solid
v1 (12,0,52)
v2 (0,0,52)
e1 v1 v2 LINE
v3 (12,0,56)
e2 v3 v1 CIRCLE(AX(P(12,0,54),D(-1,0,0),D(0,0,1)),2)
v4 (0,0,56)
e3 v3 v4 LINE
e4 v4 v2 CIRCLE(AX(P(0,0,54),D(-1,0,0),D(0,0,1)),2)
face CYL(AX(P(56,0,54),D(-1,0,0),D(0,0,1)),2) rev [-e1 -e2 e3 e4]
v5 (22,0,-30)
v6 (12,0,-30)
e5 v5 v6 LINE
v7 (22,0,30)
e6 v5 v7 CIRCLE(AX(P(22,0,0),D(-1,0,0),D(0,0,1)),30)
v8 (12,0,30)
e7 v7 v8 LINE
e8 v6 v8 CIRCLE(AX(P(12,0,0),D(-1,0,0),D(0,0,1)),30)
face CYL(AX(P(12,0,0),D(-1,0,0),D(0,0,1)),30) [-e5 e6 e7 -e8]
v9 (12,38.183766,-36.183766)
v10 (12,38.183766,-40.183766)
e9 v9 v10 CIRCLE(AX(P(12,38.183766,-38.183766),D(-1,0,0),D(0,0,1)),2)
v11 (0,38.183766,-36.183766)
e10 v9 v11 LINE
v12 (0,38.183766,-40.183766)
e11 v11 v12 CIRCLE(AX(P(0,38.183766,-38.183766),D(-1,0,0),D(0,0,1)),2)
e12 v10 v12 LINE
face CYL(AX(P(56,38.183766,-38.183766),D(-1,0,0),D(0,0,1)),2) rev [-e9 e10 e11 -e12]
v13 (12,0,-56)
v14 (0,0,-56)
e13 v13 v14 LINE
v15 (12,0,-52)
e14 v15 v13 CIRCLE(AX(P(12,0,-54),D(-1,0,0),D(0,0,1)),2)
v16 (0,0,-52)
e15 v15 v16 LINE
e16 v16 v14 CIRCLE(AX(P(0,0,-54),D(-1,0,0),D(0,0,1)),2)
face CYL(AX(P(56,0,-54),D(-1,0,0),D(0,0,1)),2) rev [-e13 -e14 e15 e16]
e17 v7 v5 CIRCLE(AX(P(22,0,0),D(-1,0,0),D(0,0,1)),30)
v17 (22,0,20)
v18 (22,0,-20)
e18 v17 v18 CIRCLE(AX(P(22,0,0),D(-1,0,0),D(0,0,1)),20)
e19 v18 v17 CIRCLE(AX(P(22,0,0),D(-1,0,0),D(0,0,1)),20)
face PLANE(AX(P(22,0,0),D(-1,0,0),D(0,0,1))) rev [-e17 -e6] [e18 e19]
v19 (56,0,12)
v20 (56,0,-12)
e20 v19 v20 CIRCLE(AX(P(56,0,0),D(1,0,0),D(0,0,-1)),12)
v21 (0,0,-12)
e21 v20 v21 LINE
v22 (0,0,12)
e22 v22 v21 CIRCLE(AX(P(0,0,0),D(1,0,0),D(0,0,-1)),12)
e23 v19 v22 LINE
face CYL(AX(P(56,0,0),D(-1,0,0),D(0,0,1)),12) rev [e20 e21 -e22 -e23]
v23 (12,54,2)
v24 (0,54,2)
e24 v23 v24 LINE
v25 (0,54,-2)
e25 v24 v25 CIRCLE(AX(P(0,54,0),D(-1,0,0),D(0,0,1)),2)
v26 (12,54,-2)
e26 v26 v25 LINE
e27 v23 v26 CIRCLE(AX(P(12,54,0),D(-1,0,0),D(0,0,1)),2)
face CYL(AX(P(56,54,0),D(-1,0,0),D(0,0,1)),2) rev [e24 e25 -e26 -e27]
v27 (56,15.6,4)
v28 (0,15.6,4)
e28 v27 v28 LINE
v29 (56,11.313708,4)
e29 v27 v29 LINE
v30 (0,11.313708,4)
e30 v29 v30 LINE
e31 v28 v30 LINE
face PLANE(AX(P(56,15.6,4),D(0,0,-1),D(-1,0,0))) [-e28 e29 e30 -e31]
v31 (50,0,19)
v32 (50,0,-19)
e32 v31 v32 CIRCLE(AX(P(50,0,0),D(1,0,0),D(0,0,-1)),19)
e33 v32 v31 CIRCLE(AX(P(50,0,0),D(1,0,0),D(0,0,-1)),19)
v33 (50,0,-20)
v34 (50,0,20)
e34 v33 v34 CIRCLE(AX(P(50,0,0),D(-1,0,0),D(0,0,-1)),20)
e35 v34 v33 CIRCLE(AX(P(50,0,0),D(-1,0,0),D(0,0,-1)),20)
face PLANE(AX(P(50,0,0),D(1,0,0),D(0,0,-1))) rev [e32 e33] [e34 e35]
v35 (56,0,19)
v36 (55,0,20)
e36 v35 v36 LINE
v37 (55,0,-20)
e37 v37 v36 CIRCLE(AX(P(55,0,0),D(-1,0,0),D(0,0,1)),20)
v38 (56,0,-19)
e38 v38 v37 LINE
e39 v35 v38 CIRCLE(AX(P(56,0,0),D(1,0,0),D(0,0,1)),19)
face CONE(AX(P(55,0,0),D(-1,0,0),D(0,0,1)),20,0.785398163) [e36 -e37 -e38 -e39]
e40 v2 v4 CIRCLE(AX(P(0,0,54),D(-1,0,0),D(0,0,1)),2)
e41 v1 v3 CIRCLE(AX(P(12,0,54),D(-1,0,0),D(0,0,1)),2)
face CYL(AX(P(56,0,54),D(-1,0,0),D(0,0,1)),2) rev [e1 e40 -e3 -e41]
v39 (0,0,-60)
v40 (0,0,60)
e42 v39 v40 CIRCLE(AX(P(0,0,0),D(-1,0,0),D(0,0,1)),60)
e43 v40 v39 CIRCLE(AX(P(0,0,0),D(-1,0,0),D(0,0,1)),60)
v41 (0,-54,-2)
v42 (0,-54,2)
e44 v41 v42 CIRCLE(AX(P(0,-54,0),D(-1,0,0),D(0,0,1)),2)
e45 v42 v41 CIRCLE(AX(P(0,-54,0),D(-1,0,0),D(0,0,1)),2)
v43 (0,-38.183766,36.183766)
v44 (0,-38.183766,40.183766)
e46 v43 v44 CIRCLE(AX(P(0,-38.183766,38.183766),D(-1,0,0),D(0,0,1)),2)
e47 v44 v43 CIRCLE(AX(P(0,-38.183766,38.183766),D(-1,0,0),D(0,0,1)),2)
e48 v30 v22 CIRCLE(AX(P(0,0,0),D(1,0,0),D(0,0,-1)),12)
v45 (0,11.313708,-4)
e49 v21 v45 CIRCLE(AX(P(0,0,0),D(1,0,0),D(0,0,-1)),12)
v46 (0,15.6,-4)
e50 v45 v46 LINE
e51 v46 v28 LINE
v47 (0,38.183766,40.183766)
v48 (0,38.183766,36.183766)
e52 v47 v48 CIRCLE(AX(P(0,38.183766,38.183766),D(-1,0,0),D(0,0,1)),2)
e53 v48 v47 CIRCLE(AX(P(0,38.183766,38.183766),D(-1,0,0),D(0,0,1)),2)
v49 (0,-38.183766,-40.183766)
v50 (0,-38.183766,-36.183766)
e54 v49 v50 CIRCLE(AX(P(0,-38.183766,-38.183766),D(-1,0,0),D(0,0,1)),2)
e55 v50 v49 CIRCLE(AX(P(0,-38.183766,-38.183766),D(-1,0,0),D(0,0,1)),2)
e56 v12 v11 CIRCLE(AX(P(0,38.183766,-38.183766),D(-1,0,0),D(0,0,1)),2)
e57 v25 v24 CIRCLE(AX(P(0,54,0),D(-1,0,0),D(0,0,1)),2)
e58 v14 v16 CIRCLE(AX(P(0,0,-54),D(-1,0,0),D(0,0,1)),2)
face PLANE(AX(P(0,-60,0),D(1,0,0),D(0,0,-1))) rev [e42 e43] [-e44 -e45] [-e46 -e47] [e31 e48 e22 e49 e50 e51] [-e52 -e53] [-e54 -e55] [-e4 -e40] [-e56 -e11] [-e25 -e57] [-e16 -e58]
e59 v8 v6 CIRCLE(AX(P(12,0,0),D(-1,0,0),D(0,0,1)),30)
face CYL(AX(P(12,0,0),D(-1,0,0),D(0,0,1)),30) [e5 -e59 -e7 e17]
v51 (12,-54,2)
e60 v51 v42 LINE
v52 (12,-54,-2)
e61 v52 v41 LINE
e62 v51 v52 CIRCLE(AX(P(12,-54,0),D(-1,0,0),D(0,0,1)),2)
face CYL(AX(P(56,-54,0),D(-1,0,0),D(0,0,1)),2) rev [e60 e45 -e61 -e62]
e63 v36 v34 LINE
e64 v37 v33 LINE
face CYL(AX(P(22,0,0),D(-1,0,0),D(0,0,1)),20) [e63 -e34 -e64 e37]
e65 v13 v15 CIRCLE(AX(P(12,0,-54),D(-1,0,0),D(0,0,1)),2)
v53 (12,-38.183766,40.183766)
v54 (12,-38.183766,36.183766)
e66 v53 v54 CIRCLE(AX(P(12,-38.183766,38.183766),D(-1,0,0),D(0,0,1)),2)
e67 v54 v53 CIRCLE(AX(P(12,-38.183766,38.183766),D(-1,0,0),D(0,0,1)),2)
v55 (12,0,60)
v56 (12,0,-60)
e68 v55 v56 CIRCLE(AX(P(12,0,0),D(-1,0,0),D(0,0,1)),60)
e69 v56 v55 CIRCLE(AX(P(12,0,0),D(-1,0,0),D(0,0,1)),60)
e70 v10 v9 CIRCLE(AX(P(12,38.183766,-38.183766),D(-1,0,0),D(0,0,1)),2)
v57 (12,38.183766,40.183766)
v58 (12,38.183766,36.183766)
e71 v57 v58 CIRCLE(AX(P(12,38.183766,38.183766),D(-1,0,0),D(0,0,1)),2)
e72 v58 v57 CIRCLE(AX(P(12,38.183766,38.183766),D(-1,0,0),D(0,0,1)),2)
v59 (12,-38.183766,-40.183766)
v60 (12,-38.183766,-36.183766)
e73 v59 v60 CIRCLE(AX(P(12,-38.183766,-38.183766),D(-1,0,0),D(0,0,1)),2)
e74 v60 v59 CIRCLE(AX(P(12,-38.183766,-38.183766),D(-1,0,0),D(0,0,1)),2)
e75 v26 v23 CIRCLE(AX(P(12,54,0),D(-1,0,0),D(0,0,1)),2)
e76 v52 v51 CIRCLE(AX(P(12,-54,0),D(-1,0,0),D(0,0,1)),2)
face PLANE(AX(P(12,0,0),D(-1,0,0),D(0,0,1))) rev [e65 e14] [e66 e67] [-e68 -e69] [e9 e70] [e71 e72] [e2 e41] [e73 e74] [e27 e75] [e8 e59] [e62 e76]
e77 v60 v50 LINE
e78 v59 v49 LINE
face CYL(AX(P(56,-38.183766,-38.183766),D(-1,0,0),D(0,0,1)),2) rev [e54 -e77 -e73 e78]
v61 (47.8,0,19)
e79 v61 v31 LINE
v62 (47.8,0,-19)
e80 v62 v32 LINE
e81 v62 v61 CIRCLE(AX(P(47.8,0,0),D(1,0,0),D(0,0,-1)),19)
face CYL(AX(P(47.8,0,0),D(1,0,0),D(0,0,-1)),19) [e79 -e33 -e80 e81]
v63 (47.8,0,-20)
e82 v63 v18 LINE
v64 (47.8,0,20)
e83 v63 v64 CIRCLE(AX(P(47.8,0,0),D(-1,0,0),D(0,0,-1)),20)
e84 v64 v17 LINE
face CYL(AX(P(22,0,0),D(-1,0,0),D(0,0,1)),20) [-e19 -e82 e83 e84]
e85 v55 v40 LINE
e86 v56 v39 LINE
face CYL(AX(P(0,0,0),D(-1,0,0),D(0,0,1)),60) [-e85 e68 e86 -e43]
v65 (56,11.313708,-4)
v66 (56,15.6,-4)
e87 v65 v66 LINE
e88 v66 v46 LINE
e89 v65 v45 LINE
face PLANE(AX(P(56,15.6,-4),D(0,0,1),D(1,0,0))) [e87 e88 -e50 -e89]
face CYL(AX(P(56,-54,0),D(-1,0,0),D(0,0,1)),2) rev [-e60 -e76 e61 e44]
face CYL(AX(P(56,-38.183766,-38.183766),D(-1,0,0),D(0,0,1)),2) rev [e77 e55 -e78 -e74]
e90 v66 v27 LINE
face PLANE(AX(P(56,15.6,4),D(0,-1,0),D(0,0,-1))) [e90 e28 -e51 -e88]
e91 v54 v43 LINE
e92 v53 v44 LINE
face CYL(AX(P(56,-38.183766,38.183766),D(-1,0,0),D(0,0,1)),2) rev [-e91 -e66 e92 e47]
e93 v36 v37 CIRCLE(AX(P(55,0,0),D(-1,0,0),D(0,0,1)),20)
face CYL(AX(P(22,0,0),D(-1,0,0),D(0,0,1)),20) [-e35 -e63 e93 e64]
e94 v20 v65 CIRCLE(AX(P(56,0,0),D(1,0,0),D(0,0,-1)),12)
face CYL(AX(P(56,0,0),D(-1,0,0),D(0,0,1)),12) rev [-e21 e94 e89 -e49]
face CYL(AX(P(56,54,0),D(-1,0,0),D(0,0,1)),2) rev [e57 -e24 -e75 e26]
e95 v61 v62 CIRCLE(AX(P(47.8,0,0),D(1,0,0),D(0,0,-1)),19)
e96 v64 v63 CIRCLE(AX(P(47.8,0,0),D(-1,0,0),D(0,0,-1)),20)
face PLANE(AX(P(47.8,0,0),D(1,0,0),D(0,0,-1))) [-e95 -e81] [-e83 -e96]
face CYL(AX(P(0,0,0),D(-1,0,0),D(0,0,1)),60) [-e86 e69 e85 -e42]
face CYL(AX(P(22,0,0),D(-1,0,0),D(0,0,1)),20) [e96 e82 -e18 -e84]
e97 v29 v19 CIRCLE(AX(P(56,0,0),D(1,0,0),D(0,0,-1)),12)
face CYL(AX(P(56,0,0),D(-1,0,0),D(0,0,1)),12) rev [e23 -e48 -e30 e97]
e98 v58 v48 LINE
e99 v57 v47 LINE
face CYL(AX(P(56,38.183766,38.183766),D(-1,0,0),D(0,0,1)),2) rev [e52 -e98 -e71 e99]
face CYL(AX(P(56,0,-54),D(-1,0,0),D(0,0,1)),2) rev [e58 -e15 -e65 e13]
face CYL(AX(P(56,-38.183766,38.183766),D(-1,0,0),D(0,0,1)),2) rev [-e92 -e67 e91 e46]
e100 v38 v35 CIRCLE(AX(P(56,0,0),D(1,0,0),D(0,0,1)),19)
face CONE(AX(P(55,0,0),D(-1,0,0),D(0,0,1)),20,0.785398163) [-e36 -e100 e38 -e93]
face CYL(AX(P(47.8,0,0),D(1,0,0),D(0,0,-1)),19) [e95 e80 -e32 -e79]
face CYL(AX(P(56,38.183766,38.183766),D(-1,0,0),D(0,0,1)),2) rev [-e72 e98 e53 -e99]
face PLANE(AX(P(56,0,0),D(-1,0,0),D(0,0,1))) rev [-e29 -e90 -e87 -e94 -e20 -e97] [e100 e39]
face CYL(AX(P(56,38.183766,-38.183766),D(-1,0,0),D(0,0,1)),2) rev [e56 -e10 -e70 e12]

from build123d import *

# Parameters (mm, degrees)
SKETCH_1_W          = 12
SKETCH_1_H          = 60
SKETCH_2_W          = 10
SKETCH_2_H          = 30
SKETCH_3_W          = 34
SKETCH_3_H          = 20
CUT_EXTRUDE_2_DEPTH = 102.666120217
CUT_EXTRUDE_START   = 50
SKETCH_6_OUTSIDE_W  = 157.742
SKETCH_6_OUTSIDE_H  = 157.742
SKETCH_6_OUTSIDE_R  = 19
CUT_EXTRUDE_4_DEPTH = 2.2
SKETCH_7_R          = 2
CUT_EXTRUDE_5_DEPTH = 102.666120217
CHAMFER_2_SIZE      = 1


with BuildPart() as part:
    # 草图1 → 旋转-薄壁2 (revolve)
    with BuildSketch(Plane.XY, mode=Mode.PRIVATE) as revolve_2_sk:
        with Locations((6, 30)):
            Rectangle(SKETCH_1_W, SKETCH_1_H)
    revolve(revolve_2_sk.sketch.rotate(Axis((0, 0, 0), (1, 0, 0)), 90), axis=Axis((0, 0, 0), (1, 0, 0)))

    # 草图2 → 旋转-薄壁4 (revolve)
    with BuildSketch(Plane.XY, mode=Mode.PRIVATE) as revolve_4_sk:
        with Locations((17, 15)):
            Rectangle(SKETCH_2_W, SKETCH_2_H)
    revolve(revolve_4_sk.sketch.rotate(Axis((12, 0, 0), (1, 0, 0)), 90), axis=Axis((12, 0, 0), (1, 0, 0)))

    # 草图3 → 旋转-薄壁5 (revolve)
    with BuildSketch(Plane.XY, mode=Mode.PRIVATE) as revolve_5_sk:
        with Locations((39, 10)):
            Rectangle(SKETCH_3_W, SKETCH_3_H)
    revolve(revolve_5_sk.sketch.rotate(Axis((22, 0, 0), (1, 0, 0)), 90), axis=Axis((22, 0, 0), (1, 0, 0)))

    # 草图4 → 切除-拉伸2 (cut, through all)
    with BuildSketch(Plane(origin=(0, 0, 0), x_dir=(0, 0, -1), z_dir=(1, 0, 0))):
        with BuildLine():
            Line((-4, 15.6), (4, 15.6))
            Line((4, 15.6), (4, 11.313708499))
            ThreePointArc((4, 11.313708499), (0, -12), (-4, 11.313708499))
            Line((-4, 11.313708499), (-4, 15.6))
        make_face()
    extrude(amount=CUT_EXTRUDE_2_DEPTH, mode=Mode.SUBTRACT)

    # 草图6 outside → 切除-拉伸4 (cut)
    with BuildSketch(Plane(origin=(0, 0, 0), x_dir=(0, 0, -1), z_dir=(1, 0, 0)).offset(CUT_EXTRUDE_START)):
        Rectangle(SKETCH_6_OUTSIDE_W, SKETCH_6_OUTSIDE_H)
        Circle(SKETCH_6_OUTSIDE_R, mode=Mode.SUBTRACT)
    extrude(amount=-CUT_EXTRUDE_4_DEPTH, mode=Mode.SUBTRACT)

    # 草图7 → 切除-拉伸5 (cut, through all)
    with BuildSketch(Plane.ZY):
        with Locations((0, 54)):
            Circle(SKETCH_7_R)
        with Locations((38.183766184, 38.183766184)):
            Circle(SKETCH_7_R)
        with Locations((54, 0)):
            Circle(SKETCH_7_R)
        with Locations((38.183766184, -38.183766184)):
            Circle(SKETCH_7_R)
        with Locations((0, -54)):
            Circle(SKETCH_7_R)
        with Locations((-38.183766184, -38.183766184)):
            Circle(SKETCH_7_R)
        with Locations((-54, 0)):
            Circle(SKETCH_7_R)
        with Locations((-38.183766184, 38.183766184)):
            Circle(SKETCH_7_R)
    extrude(amount=-CUT_EXTRUDE_5_DEPTH, mode=Mode.SUBTRACT)

    # 倒角2
    chamfer_2_edges = [part.edges().sort_by_distance(p)[0] for p in [
        (56, 0, -20),
    ]]
    chamfer(chamfer_2_edges, length=CHAMFER_2_SIZE)


solid = part.part
